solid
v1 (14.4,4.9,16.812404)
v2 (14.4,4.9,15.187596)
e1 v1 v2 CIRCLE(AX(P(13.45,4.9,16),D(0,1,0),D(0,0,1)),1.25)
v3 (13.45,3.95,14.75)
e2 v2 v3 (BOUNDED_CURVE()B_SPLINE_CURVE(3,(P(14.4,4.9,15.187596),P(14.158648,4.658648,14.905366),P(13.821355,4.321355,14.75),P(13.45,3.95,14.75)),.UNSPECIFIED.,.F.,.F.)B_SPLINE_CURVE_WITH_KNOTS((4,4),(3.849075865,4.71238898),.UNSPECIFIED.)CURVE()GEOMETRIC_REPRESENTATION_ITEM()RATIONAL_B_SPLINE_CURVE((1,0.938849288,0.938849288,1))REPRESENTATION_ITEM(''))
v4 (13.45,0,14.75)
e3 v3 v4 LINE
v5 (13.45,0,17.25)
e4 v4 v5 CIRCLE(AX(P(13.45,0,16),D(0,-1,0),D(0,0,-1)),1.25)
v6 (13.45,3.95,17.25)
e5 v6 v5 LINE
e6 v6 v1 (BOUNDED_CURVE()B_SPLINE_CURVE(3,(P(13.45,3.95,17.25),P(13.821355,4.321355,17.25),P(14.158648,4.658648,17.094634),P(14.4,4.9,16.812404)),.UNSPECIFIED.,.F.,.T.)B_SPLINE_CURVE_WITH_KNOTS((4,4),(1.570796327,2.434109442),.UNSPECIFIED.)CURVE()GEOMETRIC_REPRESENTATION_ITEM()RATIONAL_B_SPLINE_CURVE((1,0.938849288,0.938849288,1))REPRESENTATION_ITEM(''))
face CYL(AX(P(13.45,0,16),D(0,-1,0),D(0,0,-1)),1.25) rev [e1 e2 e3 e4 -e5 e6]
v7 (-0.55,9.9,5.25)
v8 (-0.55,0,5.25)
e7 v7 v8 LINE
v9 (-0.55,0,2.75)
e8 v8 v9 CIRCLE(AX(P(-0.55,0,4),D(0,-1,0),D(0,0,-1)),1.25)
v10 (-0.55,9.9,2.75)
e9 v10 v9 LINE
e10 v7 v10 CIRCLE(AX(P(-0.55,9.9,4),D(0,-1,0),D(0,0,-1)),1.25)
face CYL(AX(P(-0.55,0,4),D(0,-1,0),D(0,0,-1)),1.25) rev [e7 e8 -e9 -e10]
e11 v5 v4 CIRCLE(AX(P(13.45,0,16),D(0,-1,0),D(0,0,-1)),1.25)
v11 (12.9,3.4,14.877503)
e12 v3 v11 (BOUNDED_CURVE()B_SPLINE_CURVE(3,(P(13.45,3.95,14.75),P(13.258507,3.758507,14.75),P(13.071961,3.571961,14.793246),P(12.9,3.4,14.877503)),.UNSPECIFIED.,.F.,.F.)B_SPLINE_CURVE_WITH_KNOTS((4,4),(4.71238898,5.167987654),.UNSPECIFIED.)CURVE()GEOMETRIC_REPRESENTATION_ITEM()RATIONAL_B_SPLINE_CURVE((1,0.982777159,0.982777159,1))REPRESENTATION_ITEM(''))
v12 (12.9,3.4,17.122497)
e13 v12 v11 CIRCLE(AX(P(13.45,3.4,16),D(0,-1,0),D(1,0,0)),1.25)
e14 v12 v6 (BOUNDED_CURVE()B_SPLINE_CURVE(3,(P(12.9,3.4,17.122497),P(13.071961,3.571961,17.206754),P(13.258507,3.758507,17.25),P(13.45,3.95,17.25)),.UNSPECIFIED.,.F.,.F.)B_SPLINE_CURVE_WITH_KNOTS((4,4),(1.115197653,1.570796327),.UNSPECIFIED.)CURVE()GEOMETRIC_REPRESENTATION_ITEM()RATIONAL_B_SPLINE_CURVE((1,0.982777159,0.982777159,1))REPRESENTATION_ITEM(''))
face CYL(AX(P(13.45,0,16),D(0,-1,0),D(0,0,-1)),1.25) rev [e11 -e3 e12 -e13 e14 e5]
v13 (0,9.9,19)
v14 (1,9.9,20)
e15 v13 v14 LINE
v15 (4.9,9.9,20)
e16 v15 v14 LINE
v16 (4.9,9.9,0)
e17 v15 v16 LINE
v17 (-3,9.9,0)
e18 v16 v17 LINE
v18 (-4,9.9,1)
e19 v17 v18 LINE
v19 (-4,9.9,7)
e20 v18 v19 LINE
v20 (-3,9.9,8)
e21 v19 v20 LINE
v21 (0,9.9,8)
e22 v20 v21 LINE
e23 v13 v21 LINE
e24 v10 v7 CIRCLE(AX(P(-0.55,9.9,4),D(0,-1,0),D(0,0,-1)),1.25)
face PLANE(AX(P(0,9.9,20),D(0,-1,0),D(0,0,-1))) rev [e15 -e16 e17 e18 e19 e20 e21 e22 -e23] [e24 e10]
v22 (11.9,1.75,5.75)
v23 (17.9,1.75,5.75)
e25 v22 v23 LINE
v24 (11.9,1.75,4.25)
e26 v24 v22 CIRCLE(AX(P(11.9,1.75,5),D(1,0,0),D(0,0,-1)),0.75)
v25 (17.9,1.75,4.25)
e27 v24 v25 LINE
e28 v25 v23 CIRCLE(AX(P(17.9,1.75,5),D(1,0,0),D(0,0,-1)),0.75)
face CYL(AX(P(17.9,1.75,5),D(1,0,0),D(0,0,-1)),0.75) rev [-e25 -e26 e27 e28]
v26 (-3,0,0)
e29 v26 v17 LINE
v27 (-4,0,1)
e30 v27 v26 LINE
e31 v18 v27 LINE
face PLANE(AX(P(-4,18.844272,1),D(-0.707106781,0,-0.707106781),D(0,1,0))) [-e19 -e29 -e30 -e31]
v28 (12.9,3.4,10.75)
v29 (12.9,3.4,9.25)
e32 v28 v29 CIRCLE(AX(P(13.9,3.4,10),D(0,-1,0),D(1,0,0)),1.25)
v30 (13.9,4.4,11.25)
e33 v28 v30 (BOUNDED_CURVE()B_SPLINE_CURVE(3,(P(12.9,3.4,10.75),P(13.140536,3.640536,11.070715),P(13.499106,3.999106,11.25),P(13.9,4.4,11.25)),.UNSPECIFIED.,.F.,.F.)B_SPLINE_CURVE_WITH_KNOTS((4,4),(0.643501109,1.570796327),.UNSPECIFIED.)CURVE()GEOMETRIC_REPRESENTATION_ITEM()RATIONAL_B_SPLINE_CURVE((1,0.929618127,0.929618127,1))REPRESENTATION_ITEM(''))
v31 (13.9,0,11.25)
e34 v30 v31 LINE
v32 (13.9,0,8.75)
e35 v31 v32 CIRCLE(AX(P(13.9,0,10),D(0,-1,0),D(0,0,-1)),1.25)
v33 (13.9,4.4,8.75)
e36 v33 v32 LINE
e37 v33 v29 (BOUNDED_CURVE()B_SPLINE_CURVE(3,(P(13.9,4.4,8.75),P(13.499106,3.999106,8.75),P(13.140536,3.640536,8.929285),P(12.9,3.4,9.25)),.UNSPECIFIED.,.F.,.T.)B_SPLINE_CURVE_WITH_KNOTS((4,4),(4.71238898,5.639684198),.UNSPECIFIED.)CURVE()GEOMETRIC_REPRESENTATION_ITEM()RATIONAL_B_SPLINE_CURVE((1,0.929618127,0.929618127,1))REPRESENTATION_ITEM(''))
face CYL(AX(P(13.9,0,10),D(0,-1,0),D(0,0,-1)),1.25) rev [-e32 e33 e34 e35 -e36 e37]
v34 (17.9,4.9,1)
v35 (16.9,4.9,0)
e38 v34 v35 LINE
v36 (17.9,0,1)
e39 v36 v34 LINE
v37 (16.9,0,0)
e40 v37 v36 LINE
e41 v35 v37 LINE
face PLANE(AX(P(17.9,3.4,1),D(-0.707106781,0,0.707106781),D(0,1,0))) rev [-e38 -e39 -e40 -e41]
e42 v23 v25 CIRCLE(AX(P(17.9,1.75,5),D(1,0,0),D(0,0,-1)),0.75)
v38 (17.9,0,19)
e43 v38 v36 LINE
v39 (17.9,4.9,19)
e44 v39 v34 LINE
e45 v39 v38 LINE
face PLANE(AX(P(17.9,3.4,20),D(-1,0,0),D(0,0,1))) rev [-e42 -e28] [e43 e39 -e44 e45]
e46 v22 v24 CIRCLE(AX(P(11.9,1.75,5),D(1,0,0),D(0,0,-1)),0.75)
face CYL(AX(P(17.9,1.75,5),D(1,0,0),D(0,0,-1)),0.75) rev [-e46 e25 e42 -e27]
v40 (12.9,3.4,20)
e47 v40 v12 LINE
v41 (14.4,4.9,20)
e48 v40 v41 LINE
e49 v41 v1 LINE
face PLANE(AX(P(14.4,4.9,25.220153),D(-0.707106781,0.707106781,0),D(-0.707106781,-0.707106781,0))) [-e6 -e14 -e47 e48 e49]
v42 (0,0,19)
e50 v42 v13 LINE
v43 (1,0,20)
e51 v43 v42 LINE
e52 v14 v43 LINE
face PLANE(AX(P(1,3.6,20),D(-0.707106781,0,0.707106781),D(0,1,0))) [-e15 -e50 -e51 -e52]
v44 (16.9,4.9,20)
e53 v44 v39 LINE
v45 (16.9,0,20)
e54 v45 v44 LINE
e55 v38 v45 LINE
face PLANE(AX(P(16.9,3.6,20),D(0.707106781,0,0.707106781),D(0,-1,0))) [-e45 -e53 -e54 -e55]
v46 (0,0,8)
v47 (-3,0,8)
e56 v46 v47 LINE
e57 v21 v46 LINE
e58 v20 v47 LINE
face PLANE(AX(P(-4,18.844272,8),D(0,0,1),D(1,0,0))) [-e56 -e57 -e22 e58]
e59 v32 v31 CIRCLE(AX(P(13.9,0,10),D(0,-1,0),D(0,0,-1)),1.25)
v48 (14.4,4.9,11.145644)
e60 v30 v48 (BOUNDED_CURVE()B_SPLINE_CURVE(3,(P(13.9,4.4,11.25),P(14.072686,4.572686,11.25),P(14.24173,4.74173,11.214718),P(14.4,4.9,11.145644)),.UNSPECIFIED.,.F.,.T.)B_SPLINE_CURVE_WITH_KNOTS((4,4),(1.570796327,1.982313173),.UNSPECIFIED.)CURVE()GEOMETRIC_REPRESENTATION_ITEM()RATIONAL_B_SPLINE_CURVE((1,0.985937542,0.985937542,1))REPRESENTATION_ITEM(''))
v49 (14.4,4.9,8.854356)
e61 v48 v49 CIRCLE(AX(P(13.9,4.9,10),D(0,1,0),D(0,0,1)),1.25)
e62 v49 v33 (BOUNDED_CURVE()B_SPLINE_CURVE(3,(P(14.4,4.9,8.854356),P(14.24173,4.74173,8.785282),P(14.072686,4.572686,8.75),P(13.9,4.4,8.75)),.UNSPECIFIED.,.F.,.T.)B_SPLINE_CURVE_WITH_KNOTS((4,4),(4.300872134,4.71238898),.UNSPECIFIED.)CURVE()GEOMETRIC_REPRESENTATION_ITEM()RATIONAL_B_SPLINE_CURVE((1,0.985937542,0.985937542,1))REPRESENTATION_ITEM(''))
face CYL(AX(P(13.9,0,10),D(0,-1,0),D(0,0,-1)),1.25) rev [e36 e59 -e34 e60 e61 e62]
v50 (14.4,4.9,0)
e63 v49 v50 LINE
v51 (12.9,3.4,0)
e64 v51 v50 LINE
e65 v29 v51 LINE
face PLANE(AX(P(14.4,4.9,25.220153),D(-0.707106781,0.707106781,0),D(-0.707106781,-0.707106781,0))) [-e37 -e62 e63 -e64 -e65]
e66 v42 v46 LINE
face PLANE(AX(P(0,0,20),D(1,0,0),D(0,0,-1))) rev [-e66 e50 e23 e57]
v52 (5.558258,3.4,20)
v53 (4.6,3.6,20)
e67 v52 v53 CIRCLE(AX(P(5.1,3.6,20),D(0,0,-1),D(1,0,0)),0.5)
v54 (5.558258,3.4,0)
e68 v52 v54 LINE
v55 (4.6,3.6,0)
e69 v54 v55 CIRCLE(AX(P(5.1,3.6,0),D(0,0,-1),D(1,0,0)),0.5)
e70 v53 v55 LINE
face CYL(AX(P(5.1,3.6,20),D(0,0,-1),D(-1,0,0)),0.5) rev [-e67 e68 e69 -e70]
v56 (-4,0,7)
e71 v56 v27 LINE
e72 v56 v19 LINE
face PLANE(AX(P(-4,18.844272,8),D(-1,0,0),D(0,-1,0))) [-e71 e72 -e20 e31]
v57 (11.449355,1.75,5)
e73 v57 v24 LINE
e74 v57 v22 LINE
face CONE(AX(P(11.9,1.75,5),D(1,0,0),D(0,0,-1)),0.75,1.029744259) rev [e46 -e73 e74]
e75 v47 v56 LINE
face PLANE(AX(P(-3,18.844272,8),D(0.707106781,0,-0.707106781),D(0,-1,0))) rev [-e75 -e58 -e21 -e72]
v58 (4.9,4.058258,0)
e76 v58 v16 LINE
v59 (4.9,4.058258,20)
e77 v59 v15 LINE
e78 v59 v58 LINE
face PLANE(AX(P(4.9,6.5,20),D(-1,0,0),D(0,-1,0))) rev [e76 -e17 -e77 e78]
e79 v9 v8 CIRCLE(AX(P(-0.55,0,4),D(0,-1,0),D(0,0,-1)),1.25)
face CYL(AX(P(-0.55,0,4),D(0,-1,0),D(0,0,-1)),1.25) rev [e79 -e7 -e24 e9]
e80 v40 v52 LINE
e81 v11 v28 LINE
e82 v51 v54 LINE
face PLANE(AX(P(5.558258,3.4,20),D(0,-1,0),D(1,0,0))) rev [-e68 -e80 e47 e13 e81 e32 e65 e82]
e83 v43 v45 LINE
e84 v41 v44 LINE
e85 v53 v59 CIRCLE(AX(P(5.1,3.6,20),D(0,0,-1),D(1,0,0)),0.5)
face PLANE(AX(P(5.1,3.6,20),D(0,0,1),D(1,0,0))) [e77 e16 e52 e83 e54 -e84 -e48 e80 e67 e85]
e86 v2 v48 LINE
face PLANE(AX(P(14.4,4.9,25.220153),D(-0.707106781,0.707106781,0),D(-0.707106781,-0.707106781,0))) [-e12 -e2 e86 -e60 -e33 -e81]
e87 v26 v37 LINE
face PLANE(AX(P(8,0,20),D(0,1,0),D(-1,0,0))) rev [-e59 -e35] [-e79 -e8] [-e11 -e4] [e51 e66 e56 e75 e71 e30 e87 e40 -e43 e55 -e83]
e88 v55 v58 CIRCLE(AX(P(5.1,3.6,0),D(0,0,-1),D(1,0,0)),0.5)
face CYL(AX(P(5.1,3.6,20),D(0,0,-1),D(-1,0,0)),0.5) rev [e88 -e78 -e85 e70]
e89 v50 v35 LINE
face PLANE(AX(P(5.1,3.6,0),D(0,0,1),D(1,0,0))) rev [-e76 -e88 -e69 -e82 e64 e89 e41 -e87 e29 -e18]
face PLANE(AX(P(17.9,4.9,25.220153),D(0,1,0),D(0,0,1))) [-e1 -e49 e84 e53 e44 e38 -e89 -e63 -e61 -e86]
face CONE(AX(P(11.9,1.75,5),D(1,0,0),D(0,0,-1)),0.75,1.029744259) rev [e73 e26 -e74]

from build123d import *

# Parameters (mm, degrees)
BOSS_EXTRUDE1_DEPTH        = 20
MOVE_FACE1_BY              = 3.4
MOVE_FACE2_BY              = 9.9
BOSS_EXTRUDE2_DEPTH        = 20
M3_TAPPED_HOLE1_D          = 2.5
M3_TAPPED_HOLE1_DEPTH      = 10
M3_TAPPED_HOLE1_TIP        = 0.751075774
SKETCH13_W                 = 4
SKETCH13_H                 = 8
BOSS_EXTRUDE3_DEPTH        = 9.9
M3_TAPPED_HOLE2_D          = 2.5
M3_TAPPED_HOLE2_DEPTH      = 10
M3_TAPPED_HOLE2_TIP        = 0.751075774
CHAMFER1_SIZE              = 1
SIZE_MM_DOWEL_HOLE_0_D     = 1.5
SIZE_MM_DOWEL_HOLE_0_DEPTH = 6
SIZE_MM_DOWEL_HOLE_0_TIP   = 0.450645464


with BuildPart() as part:
    # Sketch1 → Boss-Extrude1 (new body)
    with BuildSketch(Plane.XY):
        with BuildLine():
            Line((0, 0), (0, 6.5))
            Line((0, 6.5), (4.9, 6.5))
            Line((4.9, 6.5), (4.9, 4.058257569))
            ThreePointArc((4.9, 4.058257569), (4.746446609, 3.246446609), (5.558257569, 3.4))
            Line((5.558257569, 3.4), (8, 3.4))
            Line((8, 3.4), (8, 0))
            Line((8, 0), (0, 0))
        make_face()
    extrude(amount=BOSS_EXTRUDE1_DEPTH)

    # Move Face1: a face moved outward by 3.4
    extrude(part.faces().sort_by_distance((2.45, 6.5, 10))[0], amount=MOVE_FACE1_BY, dir=(0, 1, 0))

    # Move Face2: a face moved outward by 9.9
    extrude(part.faces().sort_by_distance((8, 1.7, 10))[0], amount=MOVE_FACE2_BY, dir=(1, 0, 0))

    # Sketch10 → Boss-Extrude2 (add)
    with BuildSketch(Plane(origin=(0, 0, 0), x_dir=(-1, 0, 0), z_dir=(0, 0, -1))):
        Polygon((-17.9, 3.4), (-17.9, 4.9), (-14.4, 4.9), (-12.9, 3.4), align=None)
    extrude(amount=-BOSS_EXTRUDE2_DEPTH)

    # M3 Tapped Hole1
    with Locations(Plane(origin=(0, 0, 0), x_dir=(-1, 0, 0), z_dir=(0, -1, 0))):
        with Locations((-13.9, -10)):
            Hole(M3_TAPPED_HOLE1_D / 2, depth=M3_TAPPED_HOLE1_DEPTH)
            with Locations((0, 0, -(M3_TAPPED_HOLE1_DEPTH + M3_TAPPED_HOLE1_TIP / 2))):  # 118° drill point
                Cone(0, M3_TAPPED_HOLE1_D / 2, M3_TAPPED_HOLE1_TIP, mode=Mode.SUBTRACT)

    # Sketch13 → Boss-Extrude3 (add)
    with BuildSketch(Plane.XZ):
        with Locations((-2, 4)):
            Rectangle(SKETCH13_W, SKETCH13_H)
    extrude(amount=-BOSS_EXTRUDE3_DEPTH)

    # M3 Tapped Hole2
    with Locations(Plane(origin=(0, 0, 0), x_dir=(-1, 0, 0), z_dir=(0, -1, 0))):
        with Locations((-13.45, -16), (0.55, -4)):
            Hole(M3_TAPPED_HOLE2_D / 2, depth=M3_TAPPED_HOLE2_DEPTH)
            with Locations((0, 0, -(M3_TAPPED_HOLE2_DEPTH + M3_TAPPED_HOLE2_TIP / 2))):  # 118° drill point
                Cone(0, M3_TAPPED_HOLE2_D / 2, M3_TAPPED_HOLE2_TIP, mode=Mode.SUBTRACT)

    # Chamfer1
    chamfer1_edges = [part.edges().sort_by_distance(p)[0] for p in [
        (0, 4.95, 20),
        (-4, 4.95, 0),
        (-4, 4.95, 8),
        (17.9, 2.45, 20),
        (17.9, 2.45, 0),
    ]]
    chamfer(chamfer1_edges, length=CHAMFER1_SIZE)

    # Size mm dowel hole 0
    with Locations(Plane(origin=(17.9, 0, 0), x_dir=(0, 0, -1), z_dir=(1, 0, 0))):
        with Locations((-5, 1.75)):
            Hole(SIZE_MM_DOWEL_HOLE_0_D / 2, depth=SIZE_MM_DOWEL_HOLE_0_DEPTH)
            with Locations((0, 0, -(SIZE_MM_DOWEL_HOLE_0_DEPTH + SIZE_MM_DOWEL_HOLE_0_TIP / 2))):  # 118° drill point
                Cone(0, SIZE_MM_DOWEL_HOLE_0_D / 2, SIZE_MM_DOWEL_HOLE_0_TIP, mode=Mode.SUBTRACT)


solid = part.part
